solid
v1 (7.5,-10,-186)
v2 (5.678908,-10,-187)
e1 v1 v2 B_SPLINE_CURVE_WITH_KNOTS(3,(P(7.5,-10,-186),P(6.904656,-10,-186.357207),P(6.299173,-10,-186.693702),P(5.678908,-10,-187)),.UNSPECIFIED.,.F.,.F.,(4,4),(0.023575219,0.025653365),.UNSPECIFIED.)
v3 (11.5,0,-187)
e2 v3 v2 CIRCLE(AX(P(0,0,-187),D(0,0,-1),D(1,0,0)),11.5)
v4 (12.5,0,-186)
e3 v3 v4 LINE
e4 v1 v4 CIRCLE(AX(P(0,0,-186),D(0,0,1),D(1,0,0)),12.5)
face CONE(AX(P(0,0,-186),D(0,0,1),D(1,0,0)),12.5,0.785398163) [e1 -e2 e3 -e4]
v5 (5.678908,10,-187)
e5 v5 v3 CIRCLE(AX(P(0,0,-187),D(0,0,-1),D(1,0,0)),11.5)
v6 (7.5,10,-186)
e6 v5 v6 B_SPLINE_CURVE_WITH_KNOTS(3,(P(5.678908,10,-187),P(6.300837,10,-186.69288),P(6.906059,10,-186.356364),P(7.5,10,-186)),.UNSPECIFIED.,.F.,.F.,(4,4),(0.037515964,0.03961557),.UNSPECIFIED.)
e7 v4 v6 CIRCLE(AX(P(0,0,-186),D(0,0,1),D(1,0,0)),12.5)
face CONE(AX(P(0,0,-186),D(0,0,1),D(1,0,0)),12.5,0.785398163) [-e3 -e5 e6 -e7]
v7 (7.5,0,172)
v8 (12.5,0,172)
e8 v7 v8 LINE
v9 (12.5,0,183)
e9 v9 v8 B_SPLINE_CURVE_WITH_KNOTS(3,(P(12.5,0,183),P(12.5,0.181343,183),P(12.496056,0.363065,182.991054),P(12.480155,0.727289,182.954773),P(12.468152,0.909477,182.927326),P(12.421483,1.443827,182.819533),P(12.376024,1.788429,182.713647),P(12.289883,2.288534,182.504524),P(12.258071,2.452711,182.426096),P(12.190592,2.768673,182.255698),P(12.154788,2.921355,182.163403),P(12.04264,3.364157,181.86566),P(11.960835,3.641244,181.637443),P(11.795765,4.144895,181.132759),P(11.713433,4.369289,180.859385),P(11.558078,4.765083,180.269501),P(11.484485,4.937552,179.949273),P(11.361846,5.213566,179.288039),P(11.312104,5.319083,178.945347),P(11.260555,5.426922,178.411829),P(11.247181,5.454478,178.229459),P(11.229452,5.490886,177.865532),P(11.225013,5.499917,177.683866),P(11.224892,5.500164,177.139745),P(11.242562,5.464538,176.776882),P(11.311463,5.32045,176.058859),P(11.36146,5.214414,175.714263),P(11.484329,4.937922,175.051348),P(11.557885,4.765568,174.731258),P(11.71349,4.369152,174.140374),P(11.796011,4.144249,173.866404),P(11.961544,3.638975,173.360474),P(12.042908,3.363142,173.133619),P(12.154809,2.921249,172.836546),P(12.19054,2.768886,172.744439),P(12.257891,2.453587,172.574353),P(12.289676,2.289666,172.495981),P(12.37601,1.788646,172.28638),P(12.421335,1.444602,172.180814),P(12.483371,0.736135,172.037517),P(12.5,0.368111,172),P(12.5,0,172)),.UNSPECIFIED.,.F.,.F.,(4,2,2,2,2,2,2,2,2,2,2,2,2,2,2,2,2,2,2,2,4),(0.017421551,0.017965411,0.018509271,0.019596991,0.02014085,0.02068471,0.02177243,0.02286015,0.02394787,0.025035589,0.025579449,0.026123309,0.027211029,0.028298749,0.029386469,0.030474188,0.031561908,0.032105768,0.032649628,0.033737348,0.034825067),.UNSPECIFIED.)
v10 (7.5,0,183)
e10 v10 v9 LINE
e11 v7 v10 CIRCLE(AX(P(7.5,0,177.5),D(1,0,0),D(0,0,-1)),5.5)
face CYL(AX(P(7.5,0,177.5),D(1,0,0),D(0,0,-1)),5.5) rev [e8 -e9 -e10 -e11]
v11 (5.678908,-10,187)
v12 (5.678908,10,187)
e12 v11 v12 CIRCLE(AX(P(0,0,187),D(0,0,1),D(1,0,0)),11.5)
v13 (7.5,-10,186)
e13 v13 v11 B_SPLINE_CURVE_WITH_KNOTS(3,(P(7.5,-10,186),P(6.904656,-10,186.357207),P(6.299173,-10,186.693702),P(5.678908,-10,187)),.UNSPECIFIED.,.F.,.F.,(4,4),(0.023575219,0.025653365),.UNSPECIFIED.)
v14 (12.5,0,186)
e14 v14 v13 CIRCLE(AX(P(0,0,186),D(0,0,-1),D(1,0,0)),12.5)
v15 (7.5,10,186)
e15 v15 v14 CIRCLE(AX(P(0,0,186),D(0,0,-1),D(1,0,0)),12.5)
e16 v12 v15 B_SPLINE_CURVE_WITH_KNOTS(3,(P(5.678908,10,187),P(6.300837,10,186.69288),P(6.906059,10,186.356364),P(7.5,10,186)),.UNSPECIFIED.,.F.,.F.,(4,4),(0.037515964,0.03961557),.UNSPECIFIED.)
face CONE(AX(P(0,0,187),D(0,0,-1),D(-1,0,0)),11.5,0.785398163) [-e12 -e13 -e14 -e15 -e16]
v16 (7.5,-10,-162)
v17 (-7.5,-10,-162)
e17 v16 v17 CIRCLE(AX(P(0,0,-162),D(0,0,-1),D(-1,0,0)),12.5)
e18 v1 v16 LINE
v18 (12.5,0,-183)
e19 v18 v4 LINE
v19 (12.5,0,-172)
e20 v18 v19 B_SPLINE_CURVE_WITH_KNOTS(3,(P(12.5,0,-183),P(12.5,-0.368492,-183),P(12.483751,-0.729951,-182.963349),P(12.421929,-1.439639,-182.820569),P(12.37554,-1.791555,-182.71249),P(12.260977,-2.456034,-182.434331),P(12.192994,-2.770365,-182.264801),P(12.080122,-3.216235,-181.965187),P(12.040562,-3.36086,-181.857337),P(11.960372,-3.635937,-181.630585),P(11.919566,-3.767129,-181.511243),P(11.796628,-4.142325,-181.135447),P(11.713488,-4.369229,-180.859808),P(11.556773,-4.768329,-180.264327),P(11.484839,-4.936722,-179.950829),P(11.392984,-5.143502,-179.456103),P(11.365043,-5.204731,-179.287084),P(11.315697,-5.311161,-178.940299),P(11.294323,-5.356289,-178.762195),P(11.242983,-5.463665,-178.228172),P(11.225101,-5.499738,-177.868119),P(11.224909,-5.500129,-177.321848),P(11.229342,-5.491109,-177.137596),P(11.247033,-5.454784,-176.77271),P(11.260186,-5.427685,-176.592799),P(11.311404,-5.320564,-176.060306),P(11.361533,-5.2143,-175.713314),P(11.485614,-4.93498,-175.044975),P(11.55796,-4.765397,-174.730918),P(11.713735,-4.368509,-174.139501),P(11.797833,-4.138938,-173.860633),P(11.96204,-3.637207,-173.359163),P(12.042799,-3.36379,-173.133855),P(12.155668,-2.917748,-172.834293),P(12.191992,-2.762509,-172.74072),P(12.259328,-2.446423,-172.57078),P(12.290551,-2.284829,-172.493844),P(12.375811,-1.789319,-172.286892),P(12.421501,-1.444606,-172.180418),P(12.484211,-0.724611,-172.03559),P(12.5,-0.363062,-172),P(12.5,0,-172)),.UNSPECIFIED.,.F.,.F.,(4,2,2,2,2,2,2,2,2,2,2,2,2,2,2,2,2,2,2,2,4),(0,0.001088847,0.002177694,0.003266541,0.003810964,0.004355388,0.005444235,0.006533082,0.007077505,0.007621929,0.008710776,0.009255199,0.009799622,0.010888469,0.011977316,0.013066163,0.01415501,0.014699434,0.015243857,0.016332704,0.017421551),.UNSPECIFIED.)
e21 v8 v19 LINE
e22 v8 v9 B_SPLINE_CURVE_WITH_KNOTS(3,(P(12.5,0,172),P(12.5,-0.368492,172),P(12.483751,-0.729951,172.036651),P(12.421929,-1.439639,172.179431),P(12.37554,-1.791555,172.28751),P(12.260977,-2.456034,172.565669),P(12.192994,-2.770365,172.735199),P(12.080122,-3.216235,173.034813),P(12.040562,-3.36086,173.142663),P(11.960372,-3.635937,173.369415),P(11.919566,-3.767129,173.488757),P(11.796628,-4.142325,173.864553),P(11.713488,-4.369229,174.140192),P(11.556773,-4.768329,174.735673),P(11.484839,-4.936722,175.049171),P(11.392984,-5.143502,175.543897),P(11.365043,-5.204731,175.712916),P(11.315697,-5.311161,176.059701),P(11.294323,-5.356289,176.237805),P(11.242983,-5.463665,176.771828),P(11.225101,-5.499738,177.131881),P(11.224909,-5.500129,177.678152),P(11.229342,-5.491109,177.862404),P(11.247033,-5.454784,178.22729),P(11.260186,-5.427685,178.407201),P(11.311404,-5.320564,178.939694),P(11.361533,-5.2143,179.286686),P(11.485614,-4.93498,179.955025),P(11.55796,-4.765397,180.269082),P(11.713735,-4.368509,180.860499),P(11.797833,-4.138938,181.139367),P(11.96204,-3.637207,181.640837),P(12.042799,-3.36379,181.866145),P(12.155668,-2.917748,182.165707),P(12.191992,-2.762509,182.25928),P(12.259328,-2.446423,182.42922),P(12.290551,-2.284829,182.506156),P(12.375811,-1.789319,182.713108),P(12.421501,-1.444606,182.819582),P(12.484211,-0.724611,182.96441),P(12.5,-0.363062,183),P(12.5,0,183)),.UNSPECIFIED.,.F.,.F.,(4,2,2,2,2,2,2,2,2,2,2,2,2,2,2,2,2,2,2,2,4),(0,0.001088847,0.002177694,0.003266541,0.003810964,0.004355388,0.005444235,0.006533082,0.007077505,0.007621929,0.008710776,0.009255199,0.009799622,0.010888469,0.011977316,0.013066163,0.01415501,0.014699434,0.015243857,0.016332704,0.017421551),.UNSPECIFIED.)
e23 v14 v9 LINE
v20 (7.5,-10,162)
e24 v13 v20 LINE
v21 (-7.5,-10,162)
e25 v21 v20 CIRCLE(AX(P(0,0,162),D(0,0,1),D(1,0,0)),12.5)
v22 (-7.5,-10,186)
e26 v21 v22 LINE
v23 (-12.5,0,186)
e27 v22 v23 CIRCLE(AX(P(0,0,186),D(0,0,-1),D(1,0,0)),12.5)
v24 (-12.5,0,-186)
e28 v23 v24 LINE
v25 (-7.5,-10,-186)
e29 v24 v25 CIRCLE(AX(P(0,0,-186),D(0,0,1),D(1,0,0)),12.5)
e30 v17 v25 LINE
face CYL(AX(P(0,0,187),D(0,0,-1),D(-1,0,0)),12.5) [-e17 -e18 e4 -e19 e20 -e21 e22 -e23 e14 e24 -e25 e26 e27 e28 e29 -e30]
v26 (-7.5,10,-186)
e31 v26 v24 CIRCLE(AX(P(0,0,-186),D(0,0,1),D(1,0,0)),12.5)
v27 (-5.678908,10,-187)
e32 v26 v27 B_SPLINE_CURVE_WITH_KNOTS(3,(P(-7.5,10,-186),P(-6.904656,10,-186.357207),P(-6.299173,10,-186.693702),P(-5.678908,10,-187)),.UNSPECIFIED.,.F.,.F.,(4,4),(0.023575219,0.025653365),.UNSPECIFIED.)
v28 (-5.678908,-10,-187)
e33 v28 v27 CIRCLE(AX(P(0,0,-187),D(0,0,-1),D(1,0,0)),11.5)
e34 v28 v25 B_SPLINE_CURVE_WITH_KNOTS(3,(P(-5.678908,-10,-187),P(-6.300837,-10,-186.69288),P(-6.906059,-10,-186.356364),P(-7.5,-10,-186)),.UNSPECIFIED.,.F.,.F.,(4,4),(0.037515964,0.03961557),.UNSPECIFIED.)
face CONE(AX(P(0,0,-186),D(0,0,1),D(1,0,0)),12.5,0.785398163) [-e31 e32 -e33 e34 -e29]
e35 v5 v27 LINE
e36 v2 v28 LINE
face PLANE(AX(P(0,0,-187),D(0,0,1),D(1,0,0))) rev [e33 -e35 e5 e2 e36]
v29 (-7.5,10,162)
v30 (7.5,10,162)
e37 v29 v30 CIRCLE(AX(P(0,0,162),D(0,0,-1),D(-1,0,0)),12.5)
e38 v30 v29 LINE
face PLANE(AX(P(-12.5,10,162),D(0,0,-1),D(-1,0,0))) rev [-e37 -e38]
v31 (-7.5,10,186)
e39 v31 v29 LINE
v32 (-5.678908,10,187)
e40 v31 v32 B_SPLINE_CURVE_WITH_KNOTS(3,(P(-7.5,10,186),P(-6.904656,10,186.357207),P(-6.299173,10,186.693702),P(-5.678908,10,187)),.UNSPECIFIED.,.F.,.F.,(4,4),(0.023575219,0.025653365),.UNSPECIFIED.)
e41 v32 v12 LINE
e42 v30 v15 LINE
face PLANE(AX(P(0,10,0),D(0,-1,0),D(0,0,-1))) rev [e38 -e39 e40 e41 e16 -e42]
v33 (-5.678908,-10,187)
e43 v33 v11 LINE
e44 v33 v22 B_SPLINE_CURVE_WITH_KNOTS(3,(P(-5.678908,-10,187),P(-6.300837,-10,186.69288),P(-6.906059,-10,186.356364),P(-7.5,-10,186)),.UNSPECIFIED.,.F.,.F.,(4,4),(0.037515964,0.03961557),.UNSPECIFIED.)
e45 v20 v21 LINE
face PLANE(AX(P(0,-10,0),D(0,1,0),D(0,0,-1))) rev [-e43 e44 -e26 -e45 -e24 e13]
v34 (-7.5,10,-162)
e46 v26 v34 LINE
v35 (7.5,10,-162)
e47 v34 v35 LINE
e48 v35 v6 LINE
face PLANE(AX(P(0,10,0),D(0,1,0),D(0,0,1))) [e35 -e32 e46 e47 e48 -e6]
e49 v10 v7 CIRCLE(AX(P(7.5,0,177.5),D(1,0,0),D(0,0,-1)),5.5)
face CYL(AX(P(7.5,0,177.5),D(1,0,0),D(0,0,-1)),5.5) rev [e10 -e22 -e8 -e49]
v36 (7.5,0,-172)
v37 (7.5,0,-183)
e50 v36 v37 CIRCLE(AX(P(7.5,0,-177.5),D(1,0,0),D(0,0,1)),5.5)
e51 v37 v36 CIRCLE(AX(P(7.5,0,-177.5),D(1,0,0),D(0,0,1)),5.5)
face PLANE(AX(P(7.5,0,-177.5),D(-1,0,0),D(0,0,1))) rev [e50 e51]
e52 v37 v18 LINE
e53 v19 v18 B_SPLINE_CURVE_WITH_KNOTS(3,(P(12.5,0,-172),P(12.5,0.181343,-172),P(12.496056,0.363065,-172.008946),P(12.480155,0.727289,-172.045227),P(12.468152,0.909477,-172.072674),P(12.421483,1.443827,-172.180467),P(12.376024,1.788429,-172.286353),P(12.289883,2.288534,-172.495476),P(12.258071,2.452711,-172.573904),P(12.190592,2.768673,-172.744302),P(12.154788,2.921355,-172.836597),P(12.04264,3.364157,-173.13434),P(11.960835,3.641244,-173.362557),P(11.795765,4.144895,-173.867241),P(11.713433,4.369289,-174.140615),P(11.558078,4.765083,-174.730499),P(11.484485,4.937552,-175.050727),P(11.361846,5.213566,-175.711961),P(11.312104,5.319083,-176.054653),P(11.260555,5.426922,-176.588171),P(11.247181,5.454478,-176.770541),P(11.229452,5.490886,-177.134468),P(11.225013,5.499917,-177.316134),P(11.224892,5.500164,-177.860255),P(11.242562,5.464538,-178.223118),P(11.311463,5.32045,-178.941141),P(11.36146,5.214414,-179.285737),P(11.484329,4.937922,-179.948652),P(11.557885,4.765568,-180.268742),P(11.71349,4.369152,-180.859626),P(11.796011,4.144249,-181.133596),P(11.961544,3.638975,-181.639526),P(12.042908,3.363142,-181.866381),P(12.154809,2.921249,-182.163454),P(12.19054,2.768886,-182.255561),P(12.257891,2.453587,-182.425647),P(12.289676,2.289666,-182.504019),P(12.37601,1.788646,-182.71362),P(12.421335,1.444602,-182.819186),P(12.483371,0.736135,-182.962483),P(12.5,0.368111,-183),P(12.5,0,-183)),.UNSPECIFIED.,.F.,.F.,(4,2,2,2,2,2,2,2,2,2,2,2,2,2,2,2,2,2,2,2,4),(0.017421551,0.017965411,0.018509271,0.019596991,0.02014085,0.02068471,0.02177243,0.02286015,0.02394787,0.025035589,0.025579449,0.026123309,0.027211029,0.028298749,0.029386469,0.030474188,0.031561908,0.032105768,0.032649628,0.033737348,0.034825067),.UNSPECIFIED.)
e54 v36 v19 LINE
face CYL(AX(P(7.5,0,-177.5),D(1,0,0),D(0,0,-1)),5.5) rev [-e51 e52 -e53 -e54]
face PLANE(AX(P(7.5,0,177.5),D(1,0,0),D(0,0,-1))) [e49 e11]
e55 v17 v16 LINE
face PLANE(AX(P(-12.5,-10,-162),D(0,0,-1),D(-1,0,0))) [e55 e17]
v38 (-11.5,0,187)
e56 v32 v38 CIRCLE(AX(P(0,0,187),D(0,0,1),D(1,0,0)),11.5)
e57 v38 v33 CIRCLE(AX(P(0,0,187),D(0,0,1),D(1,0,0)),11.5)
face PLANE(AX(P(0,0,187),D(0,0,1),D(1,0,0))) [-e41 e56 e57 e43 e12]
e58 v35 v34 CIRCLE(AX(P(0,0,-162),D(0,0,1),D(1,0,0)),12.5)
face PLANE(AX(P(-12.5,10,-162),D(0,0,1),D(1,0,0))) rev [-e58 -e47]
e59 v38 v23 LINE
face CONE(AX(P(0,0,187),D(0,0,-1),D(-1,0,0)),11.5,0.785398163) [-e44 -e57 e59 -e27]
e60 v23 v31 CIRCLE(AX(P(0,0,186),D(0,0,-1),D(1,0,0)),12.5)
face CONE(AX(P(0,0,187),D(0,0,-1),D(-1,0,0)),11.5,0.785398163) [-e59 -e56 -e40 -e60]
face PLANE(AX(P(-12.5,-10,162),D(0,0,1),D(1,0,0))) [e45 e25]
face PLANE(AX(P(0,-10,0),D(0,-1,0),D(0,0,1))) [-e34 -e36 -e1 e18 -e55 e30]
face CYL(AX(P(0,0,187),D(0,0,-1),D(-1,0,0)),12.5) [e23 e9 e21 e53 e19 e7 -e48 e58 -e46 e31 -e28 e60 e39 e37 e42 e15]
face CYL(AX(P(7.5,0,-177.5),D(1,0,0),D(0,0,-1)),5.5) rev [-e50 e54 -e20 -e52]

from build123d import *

# Parameters (mm, degrees)
SKETCH_1_R          = 12.5
EXTRUDE_1_DEPTH     = 187
CHAMFER_1_SIZE      = 1
SKETCH_2_W          = 25
SKETCH_2_H          = 25
CUT_EXTRUDE_1_DEPTH = 2.5
SKETCH_3_R          = 5.5
CUT_EXTRUDE_2_DEPTH = 5


with BuildPart() as part:
    # 草图1 → 凸台-拉伸1 (new, symmetric)
    with BuildSketch(Plane.XY):
        Circle(SKETCH_1_R)
    extrude(amount=EXTRUDE_1_DEPTH, both=True)

    # 倒角1
    chamfer_1_edges = [part.edges().sort_by_distance(p)[0] for p in [
        (-12.5, 0, -187),
        (-12.5, 0, 187),
    ]]
    chamfer(chamfer_1_edges, length=CHAMFER_1_SIZE)

    # 草图2 → 切除-拉伸1 (cut)
    with BuildSketch(Plane(origin=(0, 12.5, 0), x_dir=(1, 0, 0), z_dir=(0, 1, 0))):
        with Locations((0, -174.5)):
            Rectangle(SKETCH_2_W, SKETCH_2_H)
        with Locations((0, 174.5)):
            Rectangle(SKETCH_2_W, SKETCH_2_H)
    cut_extrude_1 = extrude(amount=-CUT_EXTRUDE_1_DEPTH, mode=Mode.SUBTRACT)

    # 镜向1: 切除-拉伸1 across plane
    add(cut_extrude_1.mirror(Plane.ZX), mode=Mode.SUBTRACT)

    # 草图3 → 切除-拉伸2 (cut)
    with BuildSketch(Plane(origin=(12.5, 0, 0), x_dir=(0, 0, -1), z_dir=(1, 0, 0))):
        with Locations((-177.5, 0)):
            Circle(SKETCH_3_R)
        with Locations((177.5, 0)):
            Circle(SKETCH_3_R)
    extrude(amount=-CUT_EXTRUDE_2_DEPTH, mode=Mode.SUBTRACT)


solid = part.part
